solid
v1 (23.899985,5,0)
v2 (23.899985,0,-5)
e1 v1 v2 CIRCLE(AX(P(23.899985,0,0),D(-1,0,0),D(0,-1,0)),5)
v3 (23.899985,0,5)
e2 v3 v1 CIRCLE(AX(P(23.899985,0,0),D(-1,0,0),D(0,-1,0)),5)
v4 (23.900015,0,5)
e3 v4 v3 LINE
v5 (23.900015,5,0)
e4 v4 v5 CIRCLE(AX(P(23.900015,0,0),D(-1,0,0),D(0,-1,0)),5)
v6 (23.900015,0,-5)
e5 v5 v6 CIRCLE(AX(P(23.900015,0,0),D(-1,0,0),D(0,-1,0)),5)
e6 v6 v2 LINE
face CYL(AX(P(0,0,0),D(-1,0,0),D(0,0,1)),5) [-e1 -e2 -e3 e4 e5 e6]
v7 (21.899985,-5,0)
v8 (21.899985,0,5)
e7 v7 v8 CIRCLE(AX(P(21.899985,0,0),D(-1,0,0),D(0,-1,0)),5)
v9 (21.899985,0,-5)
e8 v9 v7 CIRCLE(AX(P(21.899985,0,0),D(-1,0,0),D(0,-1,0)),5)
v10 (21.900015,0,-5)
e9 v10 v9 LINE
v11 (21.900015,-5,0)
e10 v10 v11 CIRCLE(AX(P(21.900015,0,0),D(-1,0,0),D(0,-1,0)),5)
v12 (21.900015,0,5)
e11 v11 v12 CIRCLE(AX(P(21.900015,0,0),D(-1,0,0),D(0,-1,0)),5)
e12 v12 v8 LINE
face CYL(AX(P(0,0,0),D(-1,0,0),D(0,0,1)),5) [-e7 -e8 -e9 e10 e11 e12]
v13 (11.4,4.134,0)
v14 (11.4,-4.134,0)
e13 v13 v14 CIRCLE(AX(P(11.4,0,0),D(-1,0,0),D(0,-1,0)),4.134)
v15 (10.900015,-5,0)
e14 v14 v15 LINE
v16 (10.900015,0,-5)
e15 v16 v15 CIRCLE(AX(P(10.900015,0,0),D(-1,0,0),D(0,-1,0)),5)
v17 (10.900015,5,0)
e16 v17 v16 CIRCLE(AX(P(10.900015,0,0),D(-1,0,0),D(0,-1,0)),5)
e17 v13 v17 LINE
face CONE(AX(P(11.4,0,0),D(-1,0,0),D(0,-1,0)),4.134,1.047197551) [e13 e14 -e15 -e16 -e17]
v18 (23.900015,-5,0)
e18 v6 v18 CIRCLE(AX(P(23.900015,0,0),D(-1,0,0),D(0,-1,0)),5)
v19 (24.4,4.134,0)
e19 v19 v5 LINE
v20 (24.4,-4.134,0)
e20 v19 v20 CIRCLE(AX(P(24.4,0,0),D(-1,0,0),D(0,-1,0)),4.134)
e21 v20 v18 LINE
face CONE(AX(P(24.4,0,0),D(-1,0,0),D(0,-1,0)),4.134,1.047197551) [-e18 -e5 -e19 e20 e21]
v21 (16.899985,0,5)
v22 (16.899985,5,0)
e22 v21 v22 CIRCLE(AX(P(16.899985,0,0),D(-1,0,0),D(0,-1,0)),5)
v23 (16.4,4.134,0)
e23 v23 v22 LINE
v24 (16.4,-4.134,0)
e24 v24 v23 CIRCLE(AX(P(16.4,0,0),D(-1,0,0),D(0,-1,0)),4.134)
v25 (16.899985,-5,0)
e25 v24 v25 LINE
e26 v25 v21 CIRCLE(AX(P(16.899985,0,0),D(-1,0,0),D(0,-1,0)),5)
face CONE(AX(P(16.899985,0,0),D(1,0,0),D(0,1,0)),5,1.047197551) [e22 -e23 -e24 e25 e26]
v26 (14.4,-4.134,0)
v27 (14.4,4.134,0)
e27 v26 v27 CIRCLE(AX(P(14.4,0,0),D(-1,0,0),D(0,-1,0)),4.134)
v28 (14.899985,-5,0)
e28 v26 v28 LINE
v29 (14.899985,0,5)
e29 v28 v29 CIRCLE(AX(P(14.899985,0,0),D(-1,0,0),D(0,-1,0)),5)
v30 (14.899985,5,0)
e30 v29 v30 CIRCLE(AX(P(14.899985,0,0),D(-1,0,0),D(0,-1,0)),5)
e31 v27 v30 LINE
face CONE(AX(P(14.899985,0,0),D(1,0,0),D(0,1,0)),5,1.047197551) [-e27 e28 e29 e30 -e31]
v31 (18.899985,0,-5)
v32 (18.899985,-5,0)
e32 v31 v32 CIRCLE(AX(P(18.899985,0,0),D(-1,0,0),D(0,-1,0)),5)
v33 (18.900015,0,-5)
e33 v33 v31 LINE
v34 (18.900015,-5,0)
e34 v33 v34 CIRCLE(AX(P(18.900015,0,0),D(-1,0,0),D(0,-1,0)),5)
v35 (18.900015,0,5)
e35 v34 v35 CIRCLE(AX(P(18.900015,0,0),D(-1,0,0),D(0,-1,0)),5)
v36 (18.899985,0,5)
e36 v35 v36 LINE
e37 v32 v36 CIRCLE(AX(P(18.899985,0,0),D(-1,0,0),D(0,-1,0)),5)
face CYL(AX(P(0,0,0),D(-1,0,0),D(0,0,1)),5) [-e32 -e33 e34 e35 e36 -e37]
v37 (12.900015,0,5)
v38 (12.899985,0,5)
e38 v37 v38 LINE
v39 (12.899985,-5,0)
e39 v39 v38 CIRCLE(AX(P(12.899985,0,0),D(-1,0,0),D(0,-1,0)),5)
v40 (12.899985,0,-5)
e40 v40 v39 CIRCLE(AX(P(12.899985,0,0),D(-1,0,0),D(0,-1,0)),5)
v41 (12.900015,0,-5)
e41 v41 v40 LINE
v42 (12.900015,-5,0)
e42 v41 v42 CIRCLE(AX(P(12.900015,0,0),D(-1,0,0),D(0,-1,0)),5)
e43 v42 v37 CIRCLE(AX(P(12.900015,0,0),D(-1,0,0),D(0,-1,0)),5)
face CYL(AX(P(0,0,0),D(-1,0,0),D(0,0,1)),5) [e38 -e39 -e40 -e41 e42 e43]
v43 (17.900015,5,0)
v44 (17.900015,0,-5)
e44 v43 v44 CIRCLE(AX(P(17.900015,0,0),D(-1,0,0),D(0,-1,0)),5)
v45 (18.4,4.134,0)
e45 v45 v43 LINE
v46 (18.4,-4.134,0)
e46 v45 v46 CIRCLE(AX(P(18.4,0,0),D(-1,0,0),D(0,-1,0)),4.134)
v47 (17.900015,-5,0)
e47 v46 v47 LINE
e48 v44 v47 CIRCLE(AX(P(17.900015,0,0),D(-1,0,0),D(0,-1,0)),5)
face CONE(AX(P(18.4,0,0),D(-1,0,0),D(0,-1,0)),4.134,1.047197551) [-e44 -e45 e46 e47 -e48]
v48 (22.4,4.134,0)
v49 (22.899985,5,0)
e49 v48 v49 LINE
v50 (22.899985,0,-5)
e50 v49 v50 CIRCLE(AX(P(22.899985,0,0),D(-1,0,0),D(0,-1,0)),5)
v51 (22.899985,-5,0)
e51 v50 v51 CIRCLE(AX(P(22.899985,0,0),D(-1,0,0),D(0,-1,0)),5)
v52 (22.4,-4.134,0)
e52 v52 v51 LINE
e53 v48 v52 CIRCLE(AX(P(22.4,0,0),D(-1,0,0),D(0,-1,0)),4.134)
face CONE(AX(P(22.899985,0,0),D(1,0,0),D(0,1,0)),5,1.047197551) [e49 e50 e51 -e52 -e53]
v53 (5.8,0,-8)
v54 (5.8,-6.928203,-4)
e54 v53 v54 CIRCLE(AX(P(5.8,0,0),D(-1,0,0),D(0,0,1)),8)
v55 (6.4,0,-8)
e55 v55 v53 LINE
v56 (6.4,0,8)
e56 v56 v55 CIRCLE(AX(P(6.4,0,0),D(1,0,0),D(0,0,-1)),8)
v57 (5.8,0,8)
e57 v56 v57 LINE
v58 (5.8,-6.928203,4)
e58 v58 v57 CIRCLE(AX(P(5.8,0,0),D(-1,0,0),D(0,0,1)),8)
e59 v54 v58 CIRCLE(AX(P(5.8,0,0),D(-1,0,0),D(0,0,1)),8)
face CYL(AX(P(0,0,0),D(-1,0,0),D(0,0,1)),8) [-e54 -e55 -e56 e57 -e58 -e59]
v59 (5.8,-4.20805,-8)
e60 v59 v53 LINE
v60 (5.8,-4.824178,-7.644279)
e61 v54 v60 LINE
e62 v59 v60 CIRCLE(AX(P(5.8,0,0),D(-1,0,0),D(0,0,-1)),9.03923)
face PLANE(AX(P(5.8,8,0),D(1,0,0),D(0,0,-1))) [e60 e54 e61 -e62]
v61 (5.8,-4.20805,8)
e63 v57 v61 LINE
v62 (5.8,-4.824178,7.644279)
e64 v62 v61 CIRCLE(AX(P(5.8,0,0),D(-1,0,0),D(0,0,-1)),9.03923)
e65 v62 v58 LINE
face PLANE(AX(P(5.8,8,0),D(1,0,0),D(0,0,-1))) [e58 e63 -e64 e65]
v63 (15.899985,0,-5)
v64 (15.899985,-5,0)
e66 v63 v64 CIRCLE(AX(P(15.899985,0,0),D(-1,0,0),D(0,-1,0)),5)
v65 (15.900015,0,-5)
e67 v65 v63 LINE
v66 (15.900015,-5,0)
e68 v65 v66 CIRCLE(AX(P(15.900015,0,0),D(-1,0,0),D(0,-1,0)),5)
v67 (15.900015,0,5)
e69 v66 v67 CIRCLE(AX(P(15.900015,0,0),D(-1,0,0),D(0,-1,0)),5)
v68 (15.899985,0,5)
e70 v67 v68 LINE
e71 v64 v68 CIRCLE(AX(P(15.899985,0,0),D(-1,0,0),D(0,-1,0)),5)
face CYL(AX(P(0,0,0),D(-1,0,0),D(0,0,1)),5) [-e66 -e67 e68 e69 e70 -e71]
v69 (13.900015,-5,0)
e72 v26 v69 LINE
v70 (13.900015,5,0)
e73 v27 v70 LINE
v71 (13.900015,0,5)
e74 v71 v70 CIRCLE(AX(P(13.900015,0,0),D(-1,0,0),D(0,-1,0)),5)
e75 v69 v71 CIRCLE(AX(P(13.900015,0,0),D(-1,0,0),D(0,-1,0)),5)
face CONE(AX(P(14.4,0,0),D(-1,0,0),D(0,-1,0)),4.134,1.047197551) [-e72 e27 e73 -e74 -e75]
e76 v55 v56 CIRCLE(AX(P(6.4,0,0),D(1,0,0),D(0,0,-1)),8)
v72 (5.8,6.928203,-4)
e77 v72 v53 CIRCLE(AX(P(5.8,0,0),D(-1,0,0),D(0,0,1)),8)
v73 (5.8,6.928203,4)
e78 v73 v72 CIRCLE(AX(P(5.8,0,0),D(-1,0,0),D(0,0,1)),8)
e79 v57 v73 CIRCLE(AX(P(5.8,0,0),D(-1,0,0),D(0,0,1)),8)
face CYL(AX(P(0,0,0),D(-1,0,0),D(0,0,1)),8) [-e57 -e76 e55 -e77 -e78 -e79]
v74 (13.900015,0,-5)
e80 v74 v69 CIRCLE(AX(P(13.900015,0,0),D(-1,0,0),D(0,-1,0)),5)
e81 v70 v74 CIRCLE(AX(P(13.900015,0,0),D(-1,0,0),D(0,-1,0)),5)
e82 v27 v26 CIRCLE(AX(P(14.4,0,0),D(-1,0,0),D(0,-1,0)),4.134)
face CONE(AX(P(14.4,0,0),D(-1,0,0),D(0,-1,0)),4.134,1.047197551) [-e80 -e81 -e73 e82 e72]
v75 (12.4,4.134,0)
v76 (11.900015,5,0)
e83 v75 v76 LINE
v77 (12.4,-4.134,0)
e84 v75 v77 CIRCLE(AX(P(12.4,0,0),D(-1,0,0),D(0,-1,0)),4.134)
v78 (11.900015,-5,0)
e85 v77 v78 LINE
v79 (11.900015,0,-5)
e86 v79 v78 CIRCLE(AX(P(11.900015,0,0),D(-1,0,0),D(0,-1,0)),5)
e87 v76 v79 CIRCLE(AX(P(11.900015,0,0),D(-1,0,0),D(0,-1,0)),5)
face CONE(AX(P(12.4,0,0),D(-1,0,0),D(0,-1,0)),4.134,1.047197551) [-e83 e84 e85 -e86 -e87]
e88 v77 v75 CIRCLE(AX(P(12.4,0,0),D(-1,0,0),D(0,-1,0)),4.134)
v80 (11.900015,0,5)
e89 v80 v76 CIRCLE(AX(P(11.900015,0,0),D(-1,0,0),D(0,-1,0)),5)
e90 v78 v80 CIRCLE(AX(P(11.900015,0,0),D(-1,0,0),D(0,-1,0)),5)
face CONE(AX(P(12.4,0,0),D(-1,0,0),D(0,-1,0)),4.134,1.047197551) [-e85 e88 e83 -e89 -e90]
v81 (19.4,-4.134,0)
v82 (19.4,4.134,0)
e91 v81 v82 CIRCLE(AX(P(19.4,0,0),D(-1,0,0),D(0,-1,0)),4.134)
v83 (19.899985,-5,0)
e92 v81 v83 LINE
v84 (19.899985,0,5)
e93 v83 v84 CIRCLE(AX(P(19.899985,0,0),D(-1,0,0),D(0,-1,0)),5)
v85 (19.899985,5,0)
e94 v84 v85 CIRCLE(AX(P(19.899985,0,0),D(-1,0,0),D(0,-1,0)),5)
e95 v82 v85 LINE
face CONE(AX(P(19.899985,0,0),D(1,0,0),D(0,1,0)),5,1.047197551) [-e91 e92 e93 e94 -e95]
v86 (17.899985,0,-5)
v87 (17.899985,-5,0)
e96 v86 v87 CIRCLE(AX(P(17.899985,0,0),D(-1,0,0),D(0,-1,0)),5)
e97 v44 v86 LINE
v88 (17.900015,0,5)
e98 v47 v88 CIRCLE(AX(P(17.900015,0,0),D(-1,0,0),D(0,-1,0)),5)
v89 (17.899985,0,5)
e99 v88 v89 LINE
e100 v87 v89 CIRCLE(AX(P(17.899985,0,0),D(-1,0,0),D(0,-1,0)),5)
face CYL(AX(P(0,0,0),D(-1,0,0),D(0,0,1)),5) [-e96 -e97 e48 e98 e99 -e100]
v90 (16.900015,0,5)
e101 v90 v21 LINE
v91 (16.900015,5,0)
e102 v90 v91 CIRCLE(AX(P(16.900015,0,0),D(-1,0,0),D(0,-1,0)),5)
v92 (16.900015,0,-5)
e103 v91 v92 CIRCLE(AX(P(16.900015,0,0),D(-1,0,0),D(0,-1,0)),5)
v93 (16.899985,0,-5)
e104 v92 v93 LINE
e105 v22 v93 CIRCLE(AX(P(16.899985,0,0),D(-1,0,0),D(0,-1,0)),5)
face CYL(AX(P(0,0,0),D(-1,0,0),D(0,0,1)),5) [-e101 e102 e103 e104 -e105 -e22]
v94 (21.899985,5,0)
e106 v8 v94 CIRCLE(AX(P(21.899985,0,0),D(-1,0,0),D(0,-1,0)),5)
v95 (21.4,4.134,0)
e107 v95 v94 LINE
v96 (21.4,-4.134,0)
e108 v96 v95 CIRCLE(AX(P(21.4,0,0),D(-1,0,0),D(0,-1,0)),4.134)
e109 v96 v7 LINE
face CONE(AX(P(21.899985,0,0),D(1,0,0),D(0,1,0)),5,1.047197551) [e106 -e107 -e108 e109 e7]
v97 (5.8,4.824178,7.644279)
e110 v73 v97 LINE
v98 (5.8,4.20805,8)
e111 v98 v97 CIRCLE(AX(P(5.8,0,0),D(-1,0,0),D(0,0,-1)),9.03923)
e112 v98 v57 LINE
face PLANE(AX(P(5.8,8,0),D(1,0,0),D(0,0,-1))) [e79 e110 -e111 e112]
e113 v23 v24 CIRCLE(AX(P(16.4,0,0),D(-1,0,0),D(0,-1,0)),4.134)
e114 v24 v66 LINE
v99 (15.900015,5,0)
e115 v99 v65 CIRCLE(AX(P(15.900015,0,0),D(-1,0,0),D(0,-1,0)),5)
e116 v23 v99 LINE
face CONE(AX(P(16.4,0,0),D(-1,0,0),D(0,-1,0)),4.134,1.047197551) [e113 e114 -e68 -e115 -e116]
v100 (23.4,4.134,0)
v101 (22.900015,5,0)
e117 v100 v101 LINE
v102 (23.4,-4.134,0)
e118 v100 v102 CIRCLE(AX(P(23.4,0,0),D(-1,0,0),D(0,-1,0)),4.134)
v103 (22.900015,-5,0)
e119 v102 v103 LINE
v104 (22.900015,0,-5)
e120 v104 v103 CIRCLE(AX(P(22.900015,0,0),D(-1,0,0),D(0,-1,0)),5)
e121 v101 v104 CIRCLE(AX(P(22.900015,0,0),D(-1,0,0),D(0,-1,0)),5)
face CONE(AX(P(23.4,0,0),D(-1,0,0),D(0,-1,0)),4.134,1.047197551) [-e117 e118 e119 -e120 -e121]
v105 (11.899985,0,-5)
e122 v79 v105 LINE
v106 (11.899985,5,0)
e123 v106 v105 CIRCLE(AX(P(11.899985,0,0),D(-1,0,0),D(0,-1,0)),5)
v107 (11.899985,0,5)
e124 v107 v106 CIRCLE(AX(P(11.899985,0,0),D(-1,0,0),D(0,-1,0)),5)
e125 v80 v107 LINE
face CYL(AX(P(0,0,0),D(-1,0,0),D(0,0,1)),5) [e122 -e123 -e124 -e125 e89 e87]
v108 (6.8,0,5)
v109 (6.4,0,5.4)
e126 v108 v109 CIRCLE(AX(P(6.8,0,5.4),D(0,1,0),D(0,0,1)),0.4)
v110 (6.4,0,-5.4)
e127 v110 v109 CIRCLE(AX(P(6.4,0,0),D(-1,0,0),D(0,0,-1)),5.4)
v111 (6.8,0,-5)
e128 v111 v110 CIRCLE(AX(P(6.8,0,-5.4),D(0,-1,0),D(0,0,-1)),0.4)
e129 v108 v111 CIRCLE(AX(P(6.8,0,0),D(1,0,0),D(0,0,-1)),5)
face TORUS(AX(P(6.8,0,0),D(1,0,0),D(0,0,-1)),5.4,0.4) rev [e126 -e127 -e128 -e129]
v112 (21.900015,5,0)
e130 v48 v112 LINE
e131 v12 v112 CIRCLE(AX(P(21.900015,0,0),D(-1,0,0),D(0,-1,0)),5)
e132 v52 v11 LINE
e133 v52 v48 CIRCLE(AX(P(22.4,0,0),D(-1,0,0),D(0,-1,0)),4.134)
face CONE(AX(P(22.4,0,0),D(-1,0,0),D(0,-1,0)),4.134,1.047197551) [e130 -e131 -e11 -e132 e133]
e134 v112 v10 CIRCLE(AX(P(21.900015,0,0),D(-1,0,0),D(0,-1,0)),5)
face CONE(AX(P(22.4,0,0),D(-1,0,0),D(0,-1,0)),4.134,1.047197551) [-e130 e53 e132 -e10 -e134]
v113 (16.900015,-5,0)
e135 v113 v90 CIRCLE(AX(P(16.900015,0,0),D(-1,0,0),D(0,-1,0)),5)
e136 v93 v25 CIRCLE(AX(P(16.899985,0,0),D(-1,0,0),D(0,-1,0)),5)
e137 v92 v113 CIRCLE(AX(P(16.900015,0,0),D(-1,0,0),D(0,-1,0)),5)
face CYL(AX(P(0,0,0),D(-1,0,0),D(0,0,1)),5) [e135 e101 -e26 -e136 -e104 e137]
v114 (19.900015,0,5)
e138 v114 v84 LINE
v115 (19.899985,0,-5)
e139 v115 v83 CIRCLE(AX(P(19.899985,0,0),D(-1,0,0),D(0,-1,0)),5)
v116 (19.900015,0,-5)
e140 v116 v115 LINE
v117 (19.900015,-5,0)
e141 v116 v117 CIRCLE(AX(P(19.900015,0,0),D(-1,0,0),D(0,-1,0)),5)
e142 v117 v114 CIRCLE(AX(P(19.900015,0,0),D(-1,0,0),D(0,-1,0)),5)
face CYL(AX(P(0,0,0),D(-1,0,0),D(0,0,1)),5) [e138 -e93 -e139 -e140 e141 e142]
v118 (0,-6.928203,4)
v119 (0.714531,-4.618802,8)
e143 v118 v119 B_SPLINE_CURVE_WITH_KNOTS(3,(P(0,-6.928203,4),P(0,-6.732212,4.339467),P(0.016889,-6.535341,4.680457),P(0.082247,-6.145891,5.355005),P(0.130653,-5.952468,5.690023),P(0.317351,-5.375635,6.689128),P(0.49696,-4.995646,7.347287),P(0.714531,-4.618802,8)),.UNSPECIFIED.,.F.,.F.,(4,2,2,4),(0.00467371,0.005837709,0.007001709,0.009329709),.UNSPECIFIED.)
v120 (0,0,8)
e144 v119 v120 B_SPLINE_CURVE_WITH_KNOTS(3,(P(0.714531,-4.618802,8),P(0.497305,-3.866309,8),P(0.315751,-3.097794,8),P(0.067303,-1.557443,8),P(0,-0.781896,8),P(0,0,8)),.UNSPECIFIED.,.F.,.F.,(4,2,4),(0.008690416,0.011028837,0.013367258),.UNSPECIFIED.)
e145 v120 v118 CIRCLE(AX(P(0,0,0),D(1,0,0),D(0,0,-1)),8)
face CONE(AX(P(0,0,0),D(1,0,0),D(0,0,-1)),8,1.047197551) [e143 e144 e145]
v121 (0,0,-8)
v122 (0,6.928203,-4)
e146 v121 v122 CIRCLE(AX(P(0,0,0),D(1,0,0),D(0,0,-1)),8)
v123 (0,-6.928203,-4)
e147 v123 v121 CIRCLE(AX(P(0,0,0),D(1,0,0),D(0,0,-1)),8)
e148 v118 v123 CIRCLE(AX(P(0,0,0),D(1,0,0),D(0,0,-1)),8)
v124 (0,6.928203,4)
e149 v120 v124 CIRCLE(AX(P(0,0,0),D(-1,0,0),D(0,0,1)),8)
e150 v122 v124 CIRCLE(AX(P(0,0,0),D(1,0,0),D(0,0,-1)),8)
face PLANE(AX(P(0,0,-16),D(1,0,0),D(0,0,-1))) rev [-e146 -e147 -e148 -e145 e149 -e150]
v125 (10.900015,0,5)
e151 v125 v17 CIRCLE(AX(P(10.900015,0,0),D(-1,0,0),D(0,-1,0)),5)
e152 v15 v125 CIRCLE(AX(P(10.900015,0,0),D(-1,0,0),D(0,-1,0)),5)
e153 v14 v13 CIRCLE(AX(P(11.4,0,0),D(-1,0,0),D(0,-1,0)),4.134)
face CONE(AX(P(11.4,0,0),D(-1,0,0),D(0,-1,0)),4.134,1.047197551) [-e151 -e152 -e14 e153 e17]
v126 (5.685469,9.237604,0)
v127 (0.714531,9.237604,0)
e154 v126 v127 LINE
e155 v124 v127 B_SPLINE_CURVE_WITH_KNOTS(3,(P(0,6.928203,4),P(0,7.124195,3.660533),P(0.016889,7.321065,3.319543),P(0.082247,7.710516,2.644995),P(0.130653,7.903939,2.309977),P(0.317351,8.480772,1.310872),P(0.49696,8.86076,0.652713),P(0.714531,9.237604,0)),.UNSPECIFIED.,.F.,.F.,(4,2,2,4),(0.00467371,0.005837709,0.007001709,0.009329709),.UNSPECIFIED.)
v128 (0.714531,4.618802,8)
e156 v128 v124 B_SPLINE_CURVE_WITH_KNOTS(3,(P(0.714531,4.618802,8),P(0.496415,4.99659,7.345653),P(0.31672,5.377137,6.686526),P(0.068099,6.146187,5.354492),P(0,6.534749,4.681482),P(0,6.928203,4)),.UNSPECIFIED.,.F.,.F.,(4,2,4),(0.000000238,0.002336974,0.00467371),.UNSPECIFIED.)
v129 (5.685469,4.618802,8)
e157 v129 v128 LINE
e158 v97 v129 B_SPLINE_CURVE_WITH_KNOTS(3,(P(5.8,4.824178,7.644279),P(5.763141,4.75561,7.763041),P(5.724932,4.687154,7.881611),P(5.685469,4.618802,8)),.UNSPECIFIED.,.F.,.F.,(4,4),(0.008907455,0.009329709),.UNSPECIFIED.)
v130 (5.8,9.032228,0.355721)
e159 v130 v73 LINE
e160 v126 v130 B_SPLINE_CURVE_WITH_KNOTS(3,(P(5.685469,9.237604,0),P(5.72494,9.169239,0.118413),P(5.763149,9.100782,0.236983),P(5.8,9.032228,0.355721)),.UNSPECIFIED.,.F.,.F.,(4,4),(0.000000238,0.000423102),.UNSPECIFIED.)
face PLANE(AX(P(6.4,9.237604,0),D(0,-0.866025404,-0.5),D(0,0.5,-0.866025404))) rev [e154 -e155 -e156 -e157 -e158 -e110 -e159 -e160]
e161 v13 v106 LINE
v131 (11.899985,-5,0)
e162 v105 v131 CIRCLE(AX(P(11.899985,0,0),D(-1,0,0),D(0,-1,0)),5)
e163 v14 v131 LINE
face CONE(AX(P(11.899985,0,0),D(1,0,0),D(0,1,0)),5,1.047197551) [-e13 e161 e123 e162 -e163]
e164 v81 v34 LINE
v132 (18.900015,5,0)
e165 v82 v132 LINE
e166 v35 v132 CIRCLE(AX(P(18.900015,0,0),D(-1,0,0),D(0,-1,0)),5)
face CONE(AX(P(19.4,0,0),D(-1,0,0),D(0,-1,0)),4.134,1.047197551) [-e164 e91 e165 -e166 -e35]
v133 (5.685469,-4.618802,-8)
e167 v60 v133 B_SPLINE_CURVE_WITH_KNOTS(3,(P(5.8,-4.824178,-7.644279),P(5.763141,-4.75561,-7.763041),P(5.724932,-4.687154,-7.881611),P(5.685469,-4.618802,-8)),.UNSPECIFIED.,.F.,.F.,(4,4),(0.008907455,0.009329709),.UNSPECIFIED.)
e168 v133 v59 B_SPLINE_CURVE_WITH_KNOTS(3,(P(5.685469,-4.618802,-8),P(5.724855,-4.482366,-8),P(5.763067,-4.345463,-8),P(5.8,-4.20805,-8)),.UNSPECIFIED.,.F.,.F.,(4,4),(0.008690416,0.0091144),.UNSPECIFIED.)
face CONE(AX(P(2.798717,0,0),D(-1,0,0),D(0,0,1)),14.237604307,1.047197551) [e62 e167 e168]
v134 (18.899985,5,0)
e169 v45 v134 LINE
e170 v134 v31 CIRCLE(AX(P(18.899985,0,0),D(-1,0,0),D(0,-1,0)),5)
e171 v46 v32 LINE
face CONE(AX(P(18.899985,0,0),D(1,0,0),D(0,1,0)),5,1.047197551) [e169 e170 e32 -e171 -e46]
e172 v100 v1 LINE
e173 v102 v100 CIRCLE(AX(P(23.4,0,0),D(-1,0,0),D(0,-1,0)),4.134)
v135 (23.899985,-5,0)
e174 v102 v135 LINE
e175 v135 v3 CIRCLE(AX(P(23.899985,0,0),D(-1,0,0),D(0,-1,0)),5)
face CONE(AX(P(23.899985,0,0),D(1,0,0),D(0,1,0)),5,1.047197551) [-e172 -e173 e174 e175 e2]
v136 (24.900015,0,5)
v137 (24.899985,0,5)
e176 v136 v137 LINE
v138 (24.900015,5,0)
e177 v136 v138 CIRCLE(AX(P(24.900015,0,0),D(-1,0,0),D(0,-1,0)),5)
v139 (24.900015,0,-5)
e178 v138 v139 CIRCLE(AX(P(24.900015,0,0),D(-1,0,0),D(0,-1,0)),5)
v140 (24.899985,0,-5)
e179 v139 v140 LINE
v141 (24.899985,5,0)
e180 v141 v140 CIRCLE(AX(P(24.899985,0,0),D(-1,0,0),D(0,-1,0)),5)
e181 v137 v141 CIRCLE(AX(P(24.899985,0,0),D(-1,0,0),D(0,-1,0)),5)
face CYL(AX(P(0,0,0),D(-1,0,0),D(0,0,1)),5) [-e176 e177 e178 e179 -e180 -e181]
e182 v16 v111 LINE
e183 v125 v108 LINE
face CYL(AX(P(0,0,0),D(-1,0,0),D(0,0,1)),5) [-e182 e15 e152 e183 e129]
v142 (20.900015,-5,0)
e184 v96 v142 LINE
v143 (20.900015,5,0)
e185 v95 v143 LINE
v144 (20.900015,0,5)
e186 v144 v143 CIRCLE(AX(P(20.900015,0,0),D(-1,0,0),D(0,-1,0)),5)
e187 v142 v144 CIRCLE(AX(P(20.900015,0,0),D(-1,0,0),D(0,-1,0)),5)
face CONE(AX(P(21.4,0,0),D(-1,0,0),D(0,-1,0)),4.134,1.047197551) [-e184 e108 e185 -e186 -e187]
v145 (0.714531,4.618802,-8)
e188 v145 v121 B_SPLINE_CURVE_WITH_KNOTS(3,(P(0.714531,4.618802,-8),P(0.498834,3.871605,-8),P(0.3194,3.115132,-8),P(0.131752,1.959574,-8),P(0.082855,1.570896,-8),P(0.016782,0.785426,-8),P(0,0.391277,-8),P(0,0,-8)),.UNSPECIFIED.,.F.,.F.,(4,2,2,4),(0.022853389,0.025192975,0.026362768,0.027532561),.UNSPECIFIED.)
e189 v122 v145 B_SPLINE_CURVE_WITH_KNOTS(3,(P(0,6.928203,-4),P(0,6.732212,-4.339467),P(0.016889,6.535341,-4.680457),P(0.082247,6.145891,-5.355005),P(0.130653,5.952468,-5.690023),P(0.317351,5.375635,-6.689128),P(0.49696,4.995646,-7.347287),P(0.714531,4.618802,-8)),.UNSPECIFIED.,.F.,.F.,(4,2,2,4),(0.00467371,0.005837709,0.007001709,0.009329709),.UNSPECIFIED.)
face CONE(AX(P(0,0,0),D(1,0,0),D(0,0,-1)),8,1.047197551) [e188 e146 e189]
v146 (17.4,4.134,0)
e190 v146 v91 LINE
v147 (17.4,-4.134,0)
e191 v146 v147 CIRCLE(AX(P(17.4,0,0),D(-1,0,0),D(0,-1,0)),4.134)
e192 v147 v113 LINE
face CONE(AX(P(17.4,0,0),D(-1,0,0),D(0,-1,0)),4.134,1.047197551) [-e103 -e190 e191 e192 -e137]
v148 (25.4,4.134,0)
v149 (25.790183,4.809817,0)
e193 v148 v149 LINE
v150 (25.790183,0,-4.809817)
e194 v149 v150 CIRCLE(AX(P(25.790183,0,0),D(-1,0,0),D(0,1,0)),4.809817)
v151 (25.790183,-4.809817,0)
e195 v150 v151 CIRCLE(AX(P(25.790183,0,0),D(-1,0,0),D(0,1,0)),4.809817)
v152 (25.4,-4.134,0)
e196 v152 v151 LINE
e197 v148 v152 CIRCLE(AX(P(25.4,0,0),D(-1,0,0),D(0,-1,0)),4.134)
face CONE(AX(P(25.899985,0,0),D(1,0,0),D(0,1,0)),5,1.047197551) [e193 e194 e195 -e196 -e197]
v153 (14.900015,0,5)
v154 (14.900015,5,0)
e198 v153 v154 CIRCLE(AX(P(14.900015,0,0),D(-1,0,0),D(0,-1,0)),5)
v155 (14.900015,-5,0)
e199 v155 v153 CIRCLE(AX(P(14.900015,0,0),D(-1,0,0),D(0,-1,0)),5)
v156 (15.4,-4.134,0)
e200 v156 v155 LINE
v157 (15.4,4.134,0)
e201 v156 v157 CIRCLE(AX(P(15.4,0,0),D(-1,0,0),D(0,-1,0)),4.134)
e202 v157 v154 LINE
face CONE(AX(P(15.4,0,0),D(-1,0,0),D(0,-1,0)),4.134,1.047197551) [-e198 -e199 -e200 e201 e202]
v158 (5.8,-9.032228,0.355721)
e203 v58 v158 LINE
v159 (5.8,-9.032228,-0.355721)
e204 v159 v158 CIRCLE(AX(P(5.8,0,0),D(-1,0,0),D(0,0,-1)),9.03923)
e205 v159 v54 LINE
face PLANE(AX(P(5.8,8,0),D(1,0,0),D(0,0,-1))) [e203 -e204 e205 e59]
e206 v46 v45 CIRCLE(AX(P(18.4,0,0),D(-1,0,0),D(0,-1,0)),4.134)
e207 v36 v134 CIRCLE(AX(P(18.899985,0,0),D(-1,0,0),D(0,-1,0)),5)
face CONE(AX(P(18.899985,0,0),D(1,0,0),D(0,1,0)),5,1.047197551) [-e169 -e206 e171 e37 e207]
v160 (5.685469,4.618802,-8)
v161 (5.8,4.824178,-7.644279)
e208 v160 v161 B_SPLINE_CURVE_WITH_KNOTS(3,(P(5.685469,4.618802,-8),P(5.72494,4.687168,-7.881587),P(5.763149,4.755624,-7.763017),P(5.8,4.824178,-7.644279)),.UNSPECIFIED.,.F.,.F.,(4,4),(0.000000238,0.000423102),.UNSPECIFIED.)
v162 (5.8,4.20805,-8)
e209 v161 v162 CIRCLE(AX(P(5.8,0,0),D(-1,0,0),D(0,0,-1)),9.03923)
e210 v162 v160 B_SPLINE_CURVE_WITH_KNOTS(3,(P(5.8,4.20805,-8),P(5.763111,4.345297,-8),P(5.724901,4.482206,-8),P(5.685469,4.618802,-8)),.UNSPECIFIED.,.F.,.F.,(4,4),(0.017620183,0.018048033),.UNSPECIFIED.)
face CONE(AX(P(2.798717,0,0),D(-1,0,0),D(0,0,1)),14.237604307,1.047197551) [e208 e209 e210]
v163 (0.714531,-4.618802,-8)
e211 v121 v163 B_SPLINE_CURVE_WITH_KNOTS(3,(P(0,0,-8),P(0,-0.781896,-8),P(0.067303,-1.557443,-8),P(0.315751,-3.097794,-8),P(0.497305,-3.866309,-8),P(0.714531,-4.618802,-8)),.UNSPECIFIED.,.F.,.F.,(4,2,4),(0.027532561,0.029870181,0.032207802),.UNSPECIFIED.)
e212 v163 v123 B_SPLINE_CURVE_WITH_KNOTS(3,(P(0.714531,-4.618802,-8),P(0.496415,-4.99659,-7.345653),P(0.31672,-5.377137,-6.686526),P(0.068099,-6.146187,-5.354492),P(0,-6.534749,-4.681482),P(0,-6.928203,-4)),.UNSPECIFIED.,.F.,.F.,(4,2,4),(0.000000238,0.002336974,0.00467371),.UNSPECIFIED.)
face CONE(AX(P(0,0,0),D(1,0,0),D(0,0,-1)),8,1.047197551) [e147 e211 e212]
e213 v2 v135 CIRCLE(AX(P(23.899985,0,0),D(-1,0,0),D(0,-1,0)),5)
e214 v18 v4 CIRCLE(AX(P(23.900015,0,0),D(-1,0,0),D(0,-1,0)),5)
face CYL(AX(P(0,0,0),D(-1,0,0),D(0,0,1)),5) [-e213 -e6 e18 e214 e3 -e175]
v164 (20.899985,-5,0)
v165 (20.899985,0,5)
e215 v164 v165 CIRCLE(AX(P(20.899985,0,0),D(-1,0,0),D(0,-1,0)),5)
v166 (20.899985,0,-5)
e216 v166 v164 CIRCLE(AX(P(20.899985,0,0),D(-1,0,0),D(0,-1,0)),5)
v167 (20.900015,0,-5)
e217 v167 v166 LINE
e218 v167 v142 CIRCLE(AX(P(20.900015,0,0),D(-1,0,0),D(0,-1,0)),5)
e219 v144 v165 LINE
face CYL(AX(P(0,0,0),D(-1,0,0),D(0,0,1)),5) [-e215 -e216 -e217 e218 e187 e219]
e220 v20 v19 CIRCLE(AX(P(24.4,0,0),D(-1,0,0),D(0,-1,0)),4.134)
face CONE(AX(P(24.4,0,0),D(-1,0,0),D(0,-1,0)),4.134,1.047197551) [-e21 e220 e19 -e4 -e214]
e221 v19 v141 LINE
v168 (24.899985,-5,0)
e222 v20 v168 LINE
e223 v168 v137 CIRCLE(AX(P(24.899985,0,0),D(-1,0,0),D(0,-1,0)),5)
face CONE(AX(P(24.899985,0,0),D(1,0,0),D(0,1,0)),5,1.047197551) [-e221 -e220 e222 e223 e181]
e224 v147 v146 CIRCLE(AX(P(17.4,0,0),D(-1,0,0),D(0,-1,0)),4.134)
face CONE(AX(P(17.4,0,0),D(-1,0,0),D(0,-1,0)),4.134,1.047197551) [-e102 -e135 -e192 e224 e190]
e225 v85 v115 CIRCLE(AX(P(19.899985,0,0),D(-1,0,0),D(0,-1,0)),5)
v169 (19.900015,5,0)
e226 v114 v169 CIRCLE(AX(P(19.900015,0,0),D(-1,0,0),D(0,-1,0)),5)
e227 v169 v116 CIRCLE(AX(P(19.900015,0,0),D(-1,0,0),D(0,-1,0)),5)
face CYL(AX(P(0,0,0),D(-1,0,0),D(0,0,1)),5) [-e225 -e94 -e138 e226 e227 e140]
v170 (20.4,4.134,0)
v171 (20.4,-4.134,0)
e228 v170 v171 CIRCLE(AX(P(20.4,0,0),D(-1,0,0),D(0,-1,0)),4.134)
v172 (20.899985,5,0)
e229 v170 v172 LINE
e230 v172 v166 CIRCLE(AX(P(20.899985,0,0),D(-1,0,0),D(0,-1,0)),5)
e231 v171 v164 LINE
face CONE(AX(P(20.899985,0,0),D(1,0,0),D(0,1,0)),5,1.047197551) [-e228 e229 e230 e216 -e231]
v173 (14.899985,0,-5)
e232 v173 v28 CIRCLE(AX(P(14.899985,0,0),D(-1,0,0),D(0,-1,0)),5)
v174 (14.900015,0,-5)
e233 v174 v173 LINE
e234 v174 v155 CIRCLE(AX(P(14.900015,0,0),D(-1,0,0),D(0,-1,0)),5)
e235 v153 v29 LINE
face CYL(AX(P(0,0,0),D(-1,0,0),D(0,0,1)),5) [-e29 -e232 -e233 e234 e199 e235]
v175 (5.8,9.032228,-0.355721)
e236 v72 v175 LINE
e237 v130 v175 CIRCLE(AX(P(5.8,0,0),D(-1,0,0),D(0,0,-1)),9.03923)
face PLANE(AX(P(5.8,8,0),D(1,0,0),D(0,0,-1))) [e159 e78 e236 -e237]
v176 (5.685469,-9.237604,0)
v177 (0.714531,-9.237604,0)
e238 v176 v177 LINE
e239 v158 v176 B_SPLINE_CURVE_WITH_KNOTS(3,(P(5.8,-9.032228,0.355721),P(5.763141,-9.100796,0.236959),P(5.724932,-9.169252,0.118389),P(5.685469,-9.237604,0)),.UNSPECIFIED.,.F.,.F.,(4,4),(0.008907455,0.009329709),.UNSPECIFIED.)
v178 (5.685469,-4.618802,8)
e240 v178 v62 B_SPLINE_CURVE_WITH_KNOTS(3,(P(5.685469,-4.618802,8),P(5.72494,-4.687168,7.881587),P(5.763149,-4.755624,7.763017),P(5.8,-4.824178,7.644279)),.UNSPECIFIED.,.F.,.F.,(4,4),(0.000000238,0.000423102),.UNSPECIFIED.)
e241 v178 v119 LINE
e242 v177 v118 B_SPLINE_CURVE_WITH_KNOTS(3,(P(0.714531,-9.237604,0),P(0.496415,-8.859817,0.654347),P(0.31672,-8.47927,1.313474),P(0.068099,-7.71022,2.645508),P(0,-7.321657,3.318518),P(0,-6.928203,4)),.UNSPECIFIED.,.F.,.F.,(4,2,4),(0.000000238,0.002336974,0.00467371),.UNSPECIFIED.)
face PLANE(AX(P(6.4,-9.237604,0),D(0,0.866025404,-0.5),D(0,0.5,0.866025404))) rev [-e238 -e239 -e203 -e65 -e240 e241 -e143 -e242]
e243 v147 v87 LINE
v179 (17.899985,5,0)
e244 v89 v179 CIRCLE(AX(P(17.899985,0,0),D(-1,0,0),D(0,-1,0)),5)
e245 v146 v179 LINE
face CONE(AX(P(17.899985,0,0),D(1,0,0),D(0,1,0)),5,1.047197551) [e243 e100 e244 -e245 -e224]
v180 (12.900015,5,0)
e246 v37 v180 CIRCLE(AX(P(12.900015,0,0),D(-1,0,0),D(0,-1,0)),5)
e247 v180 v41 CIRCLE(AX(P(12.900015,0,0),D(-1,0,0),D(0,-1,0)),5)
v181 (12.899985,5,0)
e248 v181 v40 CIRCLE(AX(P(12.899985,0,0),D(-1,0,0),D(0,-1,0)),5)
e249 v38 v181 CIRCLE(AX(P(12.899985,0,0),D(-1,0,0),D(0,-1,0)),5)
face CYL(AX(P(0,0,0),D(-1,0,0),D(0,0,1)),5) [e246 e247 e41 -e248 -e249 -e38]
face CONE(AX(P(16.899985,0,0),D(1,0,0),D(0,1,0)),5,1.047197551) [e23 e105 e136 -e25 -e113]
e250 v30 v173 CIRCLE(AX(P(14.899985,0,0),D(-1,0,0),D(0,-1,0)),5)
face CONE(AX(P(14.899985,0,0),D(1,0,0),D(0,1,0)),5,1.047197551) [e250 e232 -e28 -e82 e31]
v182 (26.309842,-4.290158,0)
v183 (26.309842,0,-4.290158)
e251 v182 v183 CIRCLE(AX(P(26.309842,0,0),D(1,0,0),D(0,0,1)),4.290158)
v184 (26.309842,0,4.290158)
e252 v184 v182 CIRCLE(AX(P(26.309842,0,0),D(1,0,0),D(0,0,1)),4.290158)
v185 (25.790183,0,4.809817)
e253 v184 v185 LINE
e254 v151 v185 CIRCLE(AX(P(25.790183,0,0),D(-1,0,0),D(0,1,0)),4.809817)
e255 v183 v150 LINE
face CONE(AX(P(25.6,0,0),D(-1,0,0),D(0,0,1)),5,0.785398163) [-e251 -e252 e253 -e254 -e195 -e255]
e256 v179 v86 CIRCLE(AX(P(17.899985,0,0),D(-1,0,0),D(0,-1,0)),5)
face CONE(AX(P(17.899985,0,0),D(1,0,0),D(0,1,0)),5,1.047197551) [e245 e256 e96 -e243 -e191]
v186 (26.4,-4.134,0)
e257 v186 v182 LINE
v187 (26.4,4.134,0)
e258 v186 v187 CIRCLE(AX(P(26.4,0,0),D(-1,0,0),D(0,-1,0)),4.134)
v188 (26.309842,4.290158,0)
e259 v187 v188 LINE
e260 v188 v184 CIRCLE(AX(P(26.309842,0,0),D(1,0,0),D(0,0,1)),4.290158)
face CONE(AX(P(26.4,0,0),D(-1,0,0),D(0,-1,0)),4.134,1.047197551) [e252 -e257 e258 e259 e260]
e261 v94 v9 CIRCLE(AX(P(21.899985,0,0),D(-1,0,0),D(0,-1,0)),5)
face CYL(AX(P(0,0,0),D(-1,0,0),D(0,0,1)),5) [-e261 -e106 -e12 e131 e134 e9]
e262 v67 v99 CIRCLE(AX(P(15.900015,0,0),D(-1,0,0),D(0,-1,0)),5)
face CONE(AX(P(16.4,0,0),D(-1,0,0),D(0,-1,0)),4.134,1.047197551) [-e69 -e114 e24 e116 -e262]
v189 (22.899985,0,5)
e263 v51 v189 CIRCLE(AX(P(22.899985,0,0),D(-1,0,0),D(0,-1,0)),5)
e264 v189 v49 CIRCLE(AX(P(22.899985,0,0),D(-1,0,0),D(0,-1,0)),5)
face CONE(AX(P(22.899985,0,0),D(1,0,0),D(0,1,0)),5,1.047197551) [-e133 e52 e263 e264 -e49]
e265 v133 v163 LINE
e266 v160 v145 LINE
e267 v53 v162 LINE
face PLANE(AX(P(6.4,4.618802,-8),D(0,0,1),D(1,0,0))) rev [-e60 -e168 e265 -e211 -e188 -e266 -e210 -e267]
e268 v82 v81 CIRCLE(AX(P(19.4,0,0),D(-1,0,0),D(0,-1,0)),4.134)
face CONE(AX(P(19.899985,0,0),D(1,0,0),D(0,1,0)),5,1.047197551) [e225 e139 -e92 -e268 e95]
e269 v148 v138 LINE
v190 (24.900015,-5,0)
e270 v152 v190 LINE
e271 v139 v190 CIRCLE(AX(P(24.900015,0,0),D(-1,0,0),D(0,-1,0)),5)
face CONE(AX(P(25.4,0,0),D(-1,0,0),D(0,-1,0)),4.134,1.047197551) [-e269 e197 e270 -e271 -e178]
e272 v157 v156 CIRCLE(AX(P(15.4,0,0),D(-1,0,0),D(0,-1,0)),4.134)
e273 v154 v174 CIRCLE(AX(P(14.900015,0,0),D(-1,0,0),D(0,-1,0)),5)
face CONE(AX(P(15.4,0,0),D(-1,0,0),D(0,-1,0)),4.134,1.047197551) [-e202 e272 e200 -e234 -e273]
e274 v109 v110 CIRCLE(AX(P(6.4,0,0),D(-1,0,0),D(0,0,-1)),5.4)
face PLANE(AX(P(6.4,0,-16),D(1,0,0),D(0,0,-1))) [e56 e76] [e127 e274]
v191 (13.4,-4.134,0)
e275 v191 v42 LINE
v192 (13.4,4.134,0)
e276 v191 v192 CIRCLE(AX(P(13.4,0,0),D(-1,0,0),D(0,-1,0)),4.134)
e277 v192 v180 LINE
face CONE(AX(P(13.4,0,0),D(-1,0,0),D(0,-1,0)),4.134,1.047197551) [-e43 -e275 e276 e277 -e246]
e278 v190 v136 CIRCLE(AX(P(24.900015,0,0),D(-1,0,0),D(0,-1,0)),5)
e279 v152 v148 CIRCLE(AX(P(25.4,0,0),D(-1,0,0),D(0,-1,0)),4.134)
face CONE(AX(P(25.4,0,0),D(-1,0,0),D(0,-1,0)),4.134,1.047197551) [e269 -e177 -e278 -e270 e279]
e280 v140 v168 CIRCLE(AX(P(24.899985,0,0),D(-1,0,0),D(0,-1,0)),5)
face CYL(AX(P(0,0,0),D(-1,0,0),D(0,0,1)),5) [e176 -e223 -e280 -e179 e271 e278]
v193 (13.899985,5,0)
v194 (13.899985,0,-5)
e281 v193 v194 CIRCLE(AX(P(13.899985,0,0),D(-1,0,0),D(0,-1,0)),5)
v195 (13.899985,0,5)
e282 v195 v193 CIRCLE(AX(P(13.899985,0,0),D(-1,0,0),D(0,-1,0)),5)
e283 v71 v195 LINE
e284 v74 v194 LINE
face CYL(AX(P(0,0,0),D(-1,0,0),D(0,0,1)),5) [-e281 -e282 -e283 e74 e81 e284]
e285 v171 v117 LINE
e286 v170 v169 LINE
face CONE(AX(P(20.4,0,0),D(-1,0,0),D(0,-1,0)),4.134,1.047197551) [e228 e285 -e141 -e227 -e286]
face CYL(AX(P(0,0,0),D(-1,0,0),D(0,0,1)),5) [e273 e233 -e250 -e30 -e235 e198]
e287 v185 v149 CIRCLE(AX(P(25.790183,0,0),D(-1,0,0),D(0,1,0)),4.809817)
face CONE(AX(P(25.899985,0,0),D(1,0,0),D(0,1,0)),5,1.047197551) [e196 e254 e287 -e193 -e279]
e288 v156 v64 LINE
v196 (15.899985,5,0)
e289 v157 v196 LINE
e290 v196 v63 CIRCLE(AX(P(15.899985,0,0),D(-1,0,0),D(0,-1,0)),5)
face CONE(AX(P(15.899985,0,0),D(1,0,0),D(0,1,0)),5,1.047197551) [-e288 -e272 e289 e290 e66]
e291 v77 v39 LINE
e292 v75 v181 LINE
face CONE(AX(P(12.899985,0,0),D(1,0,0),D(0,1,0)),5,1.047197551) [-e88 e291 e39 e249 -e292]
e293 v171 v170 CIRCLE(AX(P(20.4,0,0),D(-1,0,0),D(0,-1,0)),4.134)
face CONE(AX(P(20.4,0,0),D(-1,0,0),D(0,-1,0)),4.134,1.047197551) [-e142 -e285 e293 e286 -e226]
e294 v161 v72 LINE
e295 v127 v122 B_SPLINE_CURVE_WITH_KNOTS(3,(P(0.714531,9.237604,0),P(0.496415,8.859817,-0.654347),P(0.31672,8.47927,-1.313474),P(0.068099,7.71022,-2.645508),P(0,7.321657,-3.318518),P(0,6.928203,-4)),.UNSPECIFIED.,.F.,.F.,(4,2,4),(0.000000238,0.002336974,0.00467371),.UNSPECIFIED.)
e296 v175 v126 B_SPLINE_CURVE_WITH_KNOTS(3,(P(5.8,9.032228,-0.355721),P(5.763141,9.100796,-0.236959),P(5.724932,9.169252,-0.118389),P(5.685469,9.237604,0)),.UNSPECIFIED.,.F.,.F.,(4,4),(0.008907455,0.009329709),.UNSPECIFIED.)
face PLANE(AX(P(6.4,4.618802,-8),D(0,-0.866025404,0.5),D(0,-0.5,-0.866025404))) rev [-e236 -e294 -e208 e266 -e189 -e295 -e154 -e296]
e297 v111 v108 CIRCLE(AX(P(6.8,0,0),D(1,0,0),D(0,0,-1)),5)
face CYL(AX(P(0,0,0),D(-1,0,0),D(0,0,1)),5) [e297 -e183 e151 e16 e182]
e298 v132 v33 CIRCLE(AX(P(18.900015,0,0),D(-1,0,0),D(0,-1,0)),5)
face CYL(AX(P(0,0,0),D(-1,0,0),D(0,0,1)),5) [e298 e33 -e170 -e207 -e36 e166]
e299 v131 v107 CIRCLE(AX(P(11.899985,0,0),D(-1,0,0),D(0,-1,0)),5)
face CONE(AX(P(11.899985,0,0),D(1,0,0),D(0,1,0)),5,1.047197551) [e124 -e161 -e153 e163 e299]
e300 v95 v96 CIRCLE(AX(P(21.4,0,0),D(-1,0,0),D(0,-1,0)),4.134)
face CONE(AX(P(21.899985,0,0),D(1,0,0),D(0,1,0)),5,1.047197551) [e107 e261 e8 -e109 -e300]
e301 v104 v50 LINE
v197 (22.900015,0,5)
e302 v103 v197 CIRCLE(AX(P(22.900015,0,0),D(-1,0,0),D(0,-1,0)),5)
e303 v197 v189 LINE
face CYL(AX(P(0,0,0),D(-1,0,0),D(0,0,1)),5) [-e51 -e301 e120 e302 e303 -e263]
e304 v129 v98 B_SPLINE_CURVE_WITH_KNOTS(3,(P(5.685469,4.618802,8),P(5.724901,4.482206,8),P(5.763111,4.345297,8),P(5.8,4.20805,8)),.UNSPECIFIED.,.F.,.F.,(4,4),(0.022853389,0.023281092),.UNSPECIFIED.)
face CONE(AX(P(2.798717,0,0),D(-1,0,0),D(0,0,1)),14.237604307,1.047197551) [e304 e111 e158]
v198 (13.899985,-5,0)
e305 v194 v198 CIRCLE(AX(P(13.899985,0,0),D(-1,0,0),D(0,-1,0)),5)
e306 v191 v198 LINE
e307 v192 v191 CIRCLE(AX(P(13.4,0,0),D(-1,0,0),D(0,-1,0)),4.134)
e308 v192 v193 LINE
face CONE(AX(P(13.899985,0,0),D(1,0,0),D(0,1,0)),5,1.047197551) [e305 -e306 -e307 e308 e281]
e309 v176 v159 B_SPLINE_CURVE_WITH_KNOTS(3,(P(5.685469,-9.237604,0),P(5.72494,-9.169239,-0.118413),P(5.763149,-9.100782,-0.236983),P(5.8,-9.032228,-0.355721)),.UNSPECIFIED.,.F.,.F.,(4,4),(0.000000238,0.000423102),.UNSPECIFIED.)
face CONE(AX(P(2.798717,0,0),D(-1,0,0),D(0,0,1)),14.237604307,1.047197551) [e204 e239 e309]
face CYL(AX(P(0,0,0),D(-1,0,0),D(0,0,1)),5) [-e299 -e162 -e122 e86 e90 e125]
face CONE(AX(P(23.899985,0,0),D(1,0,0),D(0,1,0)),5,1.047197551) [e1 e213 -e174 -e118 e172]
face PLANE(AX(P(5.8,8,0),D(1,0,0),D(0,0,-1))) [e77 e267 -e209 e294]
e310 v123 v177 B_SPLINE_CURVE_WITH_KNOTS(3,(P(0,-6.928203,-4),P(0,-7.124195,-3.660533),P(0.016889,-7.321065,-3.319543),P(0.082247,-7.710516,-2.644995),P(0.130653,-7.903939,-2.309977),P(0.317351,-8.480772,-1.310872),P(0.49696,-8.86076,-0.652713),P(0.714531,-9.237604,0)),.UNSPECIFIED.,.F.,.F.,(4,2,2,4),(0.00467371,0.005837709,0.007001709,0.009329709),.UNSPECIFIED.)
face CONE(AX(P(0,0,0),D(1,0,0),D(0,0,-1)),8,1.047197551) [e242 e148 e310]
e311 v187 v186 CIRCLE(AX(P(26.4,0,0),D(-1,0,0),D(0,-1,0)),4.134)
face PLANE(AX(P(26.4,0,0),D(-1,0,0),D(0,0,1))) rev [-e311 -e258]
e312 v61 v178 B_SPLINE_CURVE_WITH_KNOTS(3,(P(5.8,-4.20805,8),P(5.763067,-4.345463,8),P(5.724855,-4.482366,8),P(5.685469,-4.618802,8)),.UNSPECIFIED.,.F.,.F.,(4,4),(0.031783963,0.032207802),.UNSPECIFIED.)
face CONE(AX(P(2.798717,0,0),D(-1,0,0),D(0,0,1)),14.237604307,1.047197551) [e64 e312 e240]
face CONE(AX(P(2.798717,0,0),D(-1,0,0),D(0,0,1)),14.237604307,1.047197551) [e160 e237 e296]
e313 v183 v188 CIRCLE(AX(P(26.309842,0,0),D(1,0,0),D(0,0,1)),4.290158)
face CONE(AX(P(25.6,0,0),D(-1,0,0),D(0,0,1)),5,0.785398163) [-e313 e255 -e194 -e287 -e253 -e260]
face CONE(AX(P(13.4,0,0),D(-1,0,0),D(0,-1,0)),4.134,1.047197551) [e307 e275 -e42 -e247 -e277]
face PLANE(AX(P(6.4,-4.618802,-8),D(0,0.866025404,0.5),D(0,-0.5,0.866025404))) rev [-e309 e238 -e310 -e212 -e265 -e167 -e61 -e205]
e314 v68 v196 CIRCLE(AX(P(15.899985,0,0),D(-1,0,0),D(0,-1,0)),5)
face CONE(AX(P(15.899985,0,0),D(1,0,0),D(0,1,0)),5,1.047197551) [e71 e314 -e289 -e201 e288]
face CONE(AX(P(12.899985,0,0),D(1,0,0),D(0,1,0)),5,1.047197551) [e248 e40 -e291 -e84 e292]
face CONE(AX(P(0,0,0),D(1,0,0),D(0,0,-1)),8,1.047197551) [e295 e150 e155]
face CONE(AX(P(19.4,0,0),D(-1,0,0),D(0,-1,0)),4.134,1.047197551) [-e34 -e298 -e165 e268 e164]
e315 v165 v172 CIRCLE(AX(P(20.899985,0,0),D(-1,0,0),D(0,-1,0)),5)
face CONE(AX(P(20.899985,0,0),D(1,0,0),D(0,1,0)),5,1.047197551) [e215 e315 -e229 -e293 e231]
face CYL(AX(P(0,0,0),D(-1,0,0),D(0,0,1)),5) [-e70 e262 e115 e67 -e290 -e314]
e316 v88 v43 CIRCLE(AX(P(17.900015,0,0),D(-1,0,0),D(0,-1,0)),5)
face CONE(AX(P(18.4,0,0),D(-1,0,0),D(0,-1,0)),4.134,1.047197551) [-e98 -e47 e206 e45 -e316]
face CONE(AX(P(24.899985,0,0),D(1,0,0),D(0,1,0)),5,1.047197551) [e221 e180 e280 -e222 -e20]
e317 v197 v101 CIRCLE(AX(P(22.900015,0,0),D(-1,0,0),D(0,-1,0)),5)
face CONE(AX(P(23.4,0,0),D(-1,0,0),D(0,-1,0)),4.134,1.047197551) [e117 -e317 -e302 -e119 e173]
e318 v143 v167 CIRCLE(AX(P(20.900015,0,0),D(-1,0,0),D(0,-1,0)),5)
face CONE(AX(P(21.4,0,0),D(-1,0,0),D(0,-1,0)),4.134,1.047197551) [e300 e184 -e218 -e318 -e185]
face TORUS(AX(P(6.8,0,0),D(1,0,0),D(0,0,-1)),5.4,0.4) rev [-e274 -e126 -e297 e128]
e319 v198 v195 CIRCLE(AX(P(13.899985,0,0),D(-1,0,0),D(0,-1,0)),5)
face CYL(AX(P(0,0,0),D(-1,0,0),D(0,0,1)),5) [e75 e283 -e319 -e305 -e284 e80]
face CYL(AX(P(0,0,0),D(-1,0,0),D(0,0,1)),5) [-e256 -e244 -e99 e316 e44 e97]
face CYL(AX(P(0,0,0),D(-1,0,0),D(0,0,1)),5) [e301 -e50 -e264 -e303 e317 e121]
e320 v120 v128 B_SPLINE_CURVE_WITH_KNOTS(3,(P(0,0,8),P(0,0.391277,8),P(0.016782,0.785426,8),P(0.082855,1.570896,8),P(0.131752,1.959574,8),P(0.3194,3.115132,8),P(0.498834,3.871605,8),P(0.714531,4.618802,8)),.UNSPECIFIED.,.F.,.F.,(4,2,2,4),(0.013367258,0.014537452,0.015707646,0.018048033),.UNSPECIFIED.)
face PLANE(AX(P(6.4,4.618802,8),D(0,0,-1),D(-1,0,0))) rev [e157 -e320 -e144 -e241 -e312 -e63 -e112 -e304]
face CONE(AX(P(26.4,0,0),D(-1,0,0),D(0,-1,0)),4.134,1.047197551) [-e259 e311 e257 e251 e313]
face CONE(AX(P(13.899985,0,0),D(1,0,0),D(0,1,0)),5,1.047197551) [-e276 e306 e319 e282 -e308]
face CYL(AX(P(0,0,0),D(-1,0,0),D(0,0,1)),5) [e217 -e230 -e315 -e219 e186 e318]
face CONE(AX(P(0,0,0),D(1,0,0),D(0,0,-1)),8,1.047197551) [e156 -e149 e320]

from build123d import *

# Parameters (mm, degrees)
EXTRUDE_393_DEPTH      = 6.4
SKETCH_4_W             = 0.6
SKETCH_4_H             = 11.237604307
CHAMFER_2075_SIZE      = 0.8
FILLET_2120_R          = 0.4
PATTERN_LINEAR_1_COUNT = 16
PATTERN_LINEAR_1_PITCH = 1


with BuildPart() as part:
    # 草图1 → Extrude 393 (new body)
    with BuildSketch(Plane(origin=(0, 0, 0), x_dir=(0, 0, -1), z_dir=(1, 0, 0))):
        Polygon((8, 4.618802154), (8, -4.618802154), (0, -9.237604307), (-8, -4.618802154), (-8, 4.618802154), (0, 9.237604307), align=None)
    extrude(amount=EXTRUDE_393_DEPTH)

    # 草图2 → 凸台-旋转1 (revolve)
    with BuildSketch(Plane.XY, mode=Mode.PRIVATE) as revolve_1_sk:
        Polygon((0, 0), (26.4, 0), (26.4, 4.134), (26.4, 5), (0, 5), align=None)
    revolve(revolve_1_sk.sketch.rotate(Axis((0, 0, 0), (1, 0, 0)), 90), axis=Axis((0, 0, 0), (1, 0, 0)))

    # 草图3 → 切除-旋转1 (revolve, cut)
    with BuildSketch(Plane.XY):
        Polygon((0, 8), (3.601282526, 14.237604307), (3.601282526, 19.237604307), (-10, 19.237604307), (-10, 8), align=None)
    revolve(axis=Axis((0, 0, 0), (1, 0, 0)), mode=Mode.SUBTRACT)

    # 草图5 → 切除-旋转2 (revolve, cut)
    with BuildSketch(Plane.XY):
        Polygon((6.4, 8), (2.798717474, 14.237604307), (2.798717474, 19.237604307), (12.798717474, 19.237604307), (12.798717474, 8), align=None)
    revolve(axis=Axis((0, 0, 0), (1, 0, 0)), mode=Mode.SUBTRACT)

    # 草图4 → 切除-旋转3 (revolve, cut)
    with BuildSketch(Plane.XY, mode=Mode.PRIVATE) as cut_revolve_3_sk:
        with Locations((6.1, 13.618802154)):
            Rectangle(SKETCH_4_W, SKETCH_4_H)
    revolve(cut_revolve_3_sk.sketch.rotate(Axis((0, 0, 0), (1, 0, 0)), 270), axis=Axis((0, 0, 0), (1, 0, 0)), mode=Mode.SUBTRACT)

    # Chamfer 2075
    chamfer_2075_edges = [part.edges().sort_by_distance(p)[0] for p in [
        (26.4, 0, -5),
    ]]
    chamfer(chamfer_2075_edges, length=CHAMFER_2075_SIZE)

    # Fillet 2120
    fillet_2120_edges = [part.edges().sort_by_distance(p)[0] for p in [
        (6.4, 0, -5),
    ]]
    fillet(fillet_2120_edges, radius=FILLET_2120_R)

    # 草图6 → 切除-旋转4 (revolve, cut)
    with BuildSketch(Plane.XY):
        Polygon((11.4, -4.134), (10.900014667, -5), (10.900014667, -6.25), (11.899985333, -6.25), (11.899985333, -5), align=None)
    cut_revolve_4 = revolve(axis=Axis((-3.175, 0, 0), (1, 0, 0)), mode=Mode.SUBTRACT)

    # 阵列(线性)1: 切除-旋转4 ×16
    with Locations(*[(i * PATTERN_LINEAR_1_PITCH, 0, 0) for i in range(1, PATTERN_LINEAR_1_COUNT)]):
        add(cut_revolve_4, mode=Mode.SUBTRACT)


solid = part.part
